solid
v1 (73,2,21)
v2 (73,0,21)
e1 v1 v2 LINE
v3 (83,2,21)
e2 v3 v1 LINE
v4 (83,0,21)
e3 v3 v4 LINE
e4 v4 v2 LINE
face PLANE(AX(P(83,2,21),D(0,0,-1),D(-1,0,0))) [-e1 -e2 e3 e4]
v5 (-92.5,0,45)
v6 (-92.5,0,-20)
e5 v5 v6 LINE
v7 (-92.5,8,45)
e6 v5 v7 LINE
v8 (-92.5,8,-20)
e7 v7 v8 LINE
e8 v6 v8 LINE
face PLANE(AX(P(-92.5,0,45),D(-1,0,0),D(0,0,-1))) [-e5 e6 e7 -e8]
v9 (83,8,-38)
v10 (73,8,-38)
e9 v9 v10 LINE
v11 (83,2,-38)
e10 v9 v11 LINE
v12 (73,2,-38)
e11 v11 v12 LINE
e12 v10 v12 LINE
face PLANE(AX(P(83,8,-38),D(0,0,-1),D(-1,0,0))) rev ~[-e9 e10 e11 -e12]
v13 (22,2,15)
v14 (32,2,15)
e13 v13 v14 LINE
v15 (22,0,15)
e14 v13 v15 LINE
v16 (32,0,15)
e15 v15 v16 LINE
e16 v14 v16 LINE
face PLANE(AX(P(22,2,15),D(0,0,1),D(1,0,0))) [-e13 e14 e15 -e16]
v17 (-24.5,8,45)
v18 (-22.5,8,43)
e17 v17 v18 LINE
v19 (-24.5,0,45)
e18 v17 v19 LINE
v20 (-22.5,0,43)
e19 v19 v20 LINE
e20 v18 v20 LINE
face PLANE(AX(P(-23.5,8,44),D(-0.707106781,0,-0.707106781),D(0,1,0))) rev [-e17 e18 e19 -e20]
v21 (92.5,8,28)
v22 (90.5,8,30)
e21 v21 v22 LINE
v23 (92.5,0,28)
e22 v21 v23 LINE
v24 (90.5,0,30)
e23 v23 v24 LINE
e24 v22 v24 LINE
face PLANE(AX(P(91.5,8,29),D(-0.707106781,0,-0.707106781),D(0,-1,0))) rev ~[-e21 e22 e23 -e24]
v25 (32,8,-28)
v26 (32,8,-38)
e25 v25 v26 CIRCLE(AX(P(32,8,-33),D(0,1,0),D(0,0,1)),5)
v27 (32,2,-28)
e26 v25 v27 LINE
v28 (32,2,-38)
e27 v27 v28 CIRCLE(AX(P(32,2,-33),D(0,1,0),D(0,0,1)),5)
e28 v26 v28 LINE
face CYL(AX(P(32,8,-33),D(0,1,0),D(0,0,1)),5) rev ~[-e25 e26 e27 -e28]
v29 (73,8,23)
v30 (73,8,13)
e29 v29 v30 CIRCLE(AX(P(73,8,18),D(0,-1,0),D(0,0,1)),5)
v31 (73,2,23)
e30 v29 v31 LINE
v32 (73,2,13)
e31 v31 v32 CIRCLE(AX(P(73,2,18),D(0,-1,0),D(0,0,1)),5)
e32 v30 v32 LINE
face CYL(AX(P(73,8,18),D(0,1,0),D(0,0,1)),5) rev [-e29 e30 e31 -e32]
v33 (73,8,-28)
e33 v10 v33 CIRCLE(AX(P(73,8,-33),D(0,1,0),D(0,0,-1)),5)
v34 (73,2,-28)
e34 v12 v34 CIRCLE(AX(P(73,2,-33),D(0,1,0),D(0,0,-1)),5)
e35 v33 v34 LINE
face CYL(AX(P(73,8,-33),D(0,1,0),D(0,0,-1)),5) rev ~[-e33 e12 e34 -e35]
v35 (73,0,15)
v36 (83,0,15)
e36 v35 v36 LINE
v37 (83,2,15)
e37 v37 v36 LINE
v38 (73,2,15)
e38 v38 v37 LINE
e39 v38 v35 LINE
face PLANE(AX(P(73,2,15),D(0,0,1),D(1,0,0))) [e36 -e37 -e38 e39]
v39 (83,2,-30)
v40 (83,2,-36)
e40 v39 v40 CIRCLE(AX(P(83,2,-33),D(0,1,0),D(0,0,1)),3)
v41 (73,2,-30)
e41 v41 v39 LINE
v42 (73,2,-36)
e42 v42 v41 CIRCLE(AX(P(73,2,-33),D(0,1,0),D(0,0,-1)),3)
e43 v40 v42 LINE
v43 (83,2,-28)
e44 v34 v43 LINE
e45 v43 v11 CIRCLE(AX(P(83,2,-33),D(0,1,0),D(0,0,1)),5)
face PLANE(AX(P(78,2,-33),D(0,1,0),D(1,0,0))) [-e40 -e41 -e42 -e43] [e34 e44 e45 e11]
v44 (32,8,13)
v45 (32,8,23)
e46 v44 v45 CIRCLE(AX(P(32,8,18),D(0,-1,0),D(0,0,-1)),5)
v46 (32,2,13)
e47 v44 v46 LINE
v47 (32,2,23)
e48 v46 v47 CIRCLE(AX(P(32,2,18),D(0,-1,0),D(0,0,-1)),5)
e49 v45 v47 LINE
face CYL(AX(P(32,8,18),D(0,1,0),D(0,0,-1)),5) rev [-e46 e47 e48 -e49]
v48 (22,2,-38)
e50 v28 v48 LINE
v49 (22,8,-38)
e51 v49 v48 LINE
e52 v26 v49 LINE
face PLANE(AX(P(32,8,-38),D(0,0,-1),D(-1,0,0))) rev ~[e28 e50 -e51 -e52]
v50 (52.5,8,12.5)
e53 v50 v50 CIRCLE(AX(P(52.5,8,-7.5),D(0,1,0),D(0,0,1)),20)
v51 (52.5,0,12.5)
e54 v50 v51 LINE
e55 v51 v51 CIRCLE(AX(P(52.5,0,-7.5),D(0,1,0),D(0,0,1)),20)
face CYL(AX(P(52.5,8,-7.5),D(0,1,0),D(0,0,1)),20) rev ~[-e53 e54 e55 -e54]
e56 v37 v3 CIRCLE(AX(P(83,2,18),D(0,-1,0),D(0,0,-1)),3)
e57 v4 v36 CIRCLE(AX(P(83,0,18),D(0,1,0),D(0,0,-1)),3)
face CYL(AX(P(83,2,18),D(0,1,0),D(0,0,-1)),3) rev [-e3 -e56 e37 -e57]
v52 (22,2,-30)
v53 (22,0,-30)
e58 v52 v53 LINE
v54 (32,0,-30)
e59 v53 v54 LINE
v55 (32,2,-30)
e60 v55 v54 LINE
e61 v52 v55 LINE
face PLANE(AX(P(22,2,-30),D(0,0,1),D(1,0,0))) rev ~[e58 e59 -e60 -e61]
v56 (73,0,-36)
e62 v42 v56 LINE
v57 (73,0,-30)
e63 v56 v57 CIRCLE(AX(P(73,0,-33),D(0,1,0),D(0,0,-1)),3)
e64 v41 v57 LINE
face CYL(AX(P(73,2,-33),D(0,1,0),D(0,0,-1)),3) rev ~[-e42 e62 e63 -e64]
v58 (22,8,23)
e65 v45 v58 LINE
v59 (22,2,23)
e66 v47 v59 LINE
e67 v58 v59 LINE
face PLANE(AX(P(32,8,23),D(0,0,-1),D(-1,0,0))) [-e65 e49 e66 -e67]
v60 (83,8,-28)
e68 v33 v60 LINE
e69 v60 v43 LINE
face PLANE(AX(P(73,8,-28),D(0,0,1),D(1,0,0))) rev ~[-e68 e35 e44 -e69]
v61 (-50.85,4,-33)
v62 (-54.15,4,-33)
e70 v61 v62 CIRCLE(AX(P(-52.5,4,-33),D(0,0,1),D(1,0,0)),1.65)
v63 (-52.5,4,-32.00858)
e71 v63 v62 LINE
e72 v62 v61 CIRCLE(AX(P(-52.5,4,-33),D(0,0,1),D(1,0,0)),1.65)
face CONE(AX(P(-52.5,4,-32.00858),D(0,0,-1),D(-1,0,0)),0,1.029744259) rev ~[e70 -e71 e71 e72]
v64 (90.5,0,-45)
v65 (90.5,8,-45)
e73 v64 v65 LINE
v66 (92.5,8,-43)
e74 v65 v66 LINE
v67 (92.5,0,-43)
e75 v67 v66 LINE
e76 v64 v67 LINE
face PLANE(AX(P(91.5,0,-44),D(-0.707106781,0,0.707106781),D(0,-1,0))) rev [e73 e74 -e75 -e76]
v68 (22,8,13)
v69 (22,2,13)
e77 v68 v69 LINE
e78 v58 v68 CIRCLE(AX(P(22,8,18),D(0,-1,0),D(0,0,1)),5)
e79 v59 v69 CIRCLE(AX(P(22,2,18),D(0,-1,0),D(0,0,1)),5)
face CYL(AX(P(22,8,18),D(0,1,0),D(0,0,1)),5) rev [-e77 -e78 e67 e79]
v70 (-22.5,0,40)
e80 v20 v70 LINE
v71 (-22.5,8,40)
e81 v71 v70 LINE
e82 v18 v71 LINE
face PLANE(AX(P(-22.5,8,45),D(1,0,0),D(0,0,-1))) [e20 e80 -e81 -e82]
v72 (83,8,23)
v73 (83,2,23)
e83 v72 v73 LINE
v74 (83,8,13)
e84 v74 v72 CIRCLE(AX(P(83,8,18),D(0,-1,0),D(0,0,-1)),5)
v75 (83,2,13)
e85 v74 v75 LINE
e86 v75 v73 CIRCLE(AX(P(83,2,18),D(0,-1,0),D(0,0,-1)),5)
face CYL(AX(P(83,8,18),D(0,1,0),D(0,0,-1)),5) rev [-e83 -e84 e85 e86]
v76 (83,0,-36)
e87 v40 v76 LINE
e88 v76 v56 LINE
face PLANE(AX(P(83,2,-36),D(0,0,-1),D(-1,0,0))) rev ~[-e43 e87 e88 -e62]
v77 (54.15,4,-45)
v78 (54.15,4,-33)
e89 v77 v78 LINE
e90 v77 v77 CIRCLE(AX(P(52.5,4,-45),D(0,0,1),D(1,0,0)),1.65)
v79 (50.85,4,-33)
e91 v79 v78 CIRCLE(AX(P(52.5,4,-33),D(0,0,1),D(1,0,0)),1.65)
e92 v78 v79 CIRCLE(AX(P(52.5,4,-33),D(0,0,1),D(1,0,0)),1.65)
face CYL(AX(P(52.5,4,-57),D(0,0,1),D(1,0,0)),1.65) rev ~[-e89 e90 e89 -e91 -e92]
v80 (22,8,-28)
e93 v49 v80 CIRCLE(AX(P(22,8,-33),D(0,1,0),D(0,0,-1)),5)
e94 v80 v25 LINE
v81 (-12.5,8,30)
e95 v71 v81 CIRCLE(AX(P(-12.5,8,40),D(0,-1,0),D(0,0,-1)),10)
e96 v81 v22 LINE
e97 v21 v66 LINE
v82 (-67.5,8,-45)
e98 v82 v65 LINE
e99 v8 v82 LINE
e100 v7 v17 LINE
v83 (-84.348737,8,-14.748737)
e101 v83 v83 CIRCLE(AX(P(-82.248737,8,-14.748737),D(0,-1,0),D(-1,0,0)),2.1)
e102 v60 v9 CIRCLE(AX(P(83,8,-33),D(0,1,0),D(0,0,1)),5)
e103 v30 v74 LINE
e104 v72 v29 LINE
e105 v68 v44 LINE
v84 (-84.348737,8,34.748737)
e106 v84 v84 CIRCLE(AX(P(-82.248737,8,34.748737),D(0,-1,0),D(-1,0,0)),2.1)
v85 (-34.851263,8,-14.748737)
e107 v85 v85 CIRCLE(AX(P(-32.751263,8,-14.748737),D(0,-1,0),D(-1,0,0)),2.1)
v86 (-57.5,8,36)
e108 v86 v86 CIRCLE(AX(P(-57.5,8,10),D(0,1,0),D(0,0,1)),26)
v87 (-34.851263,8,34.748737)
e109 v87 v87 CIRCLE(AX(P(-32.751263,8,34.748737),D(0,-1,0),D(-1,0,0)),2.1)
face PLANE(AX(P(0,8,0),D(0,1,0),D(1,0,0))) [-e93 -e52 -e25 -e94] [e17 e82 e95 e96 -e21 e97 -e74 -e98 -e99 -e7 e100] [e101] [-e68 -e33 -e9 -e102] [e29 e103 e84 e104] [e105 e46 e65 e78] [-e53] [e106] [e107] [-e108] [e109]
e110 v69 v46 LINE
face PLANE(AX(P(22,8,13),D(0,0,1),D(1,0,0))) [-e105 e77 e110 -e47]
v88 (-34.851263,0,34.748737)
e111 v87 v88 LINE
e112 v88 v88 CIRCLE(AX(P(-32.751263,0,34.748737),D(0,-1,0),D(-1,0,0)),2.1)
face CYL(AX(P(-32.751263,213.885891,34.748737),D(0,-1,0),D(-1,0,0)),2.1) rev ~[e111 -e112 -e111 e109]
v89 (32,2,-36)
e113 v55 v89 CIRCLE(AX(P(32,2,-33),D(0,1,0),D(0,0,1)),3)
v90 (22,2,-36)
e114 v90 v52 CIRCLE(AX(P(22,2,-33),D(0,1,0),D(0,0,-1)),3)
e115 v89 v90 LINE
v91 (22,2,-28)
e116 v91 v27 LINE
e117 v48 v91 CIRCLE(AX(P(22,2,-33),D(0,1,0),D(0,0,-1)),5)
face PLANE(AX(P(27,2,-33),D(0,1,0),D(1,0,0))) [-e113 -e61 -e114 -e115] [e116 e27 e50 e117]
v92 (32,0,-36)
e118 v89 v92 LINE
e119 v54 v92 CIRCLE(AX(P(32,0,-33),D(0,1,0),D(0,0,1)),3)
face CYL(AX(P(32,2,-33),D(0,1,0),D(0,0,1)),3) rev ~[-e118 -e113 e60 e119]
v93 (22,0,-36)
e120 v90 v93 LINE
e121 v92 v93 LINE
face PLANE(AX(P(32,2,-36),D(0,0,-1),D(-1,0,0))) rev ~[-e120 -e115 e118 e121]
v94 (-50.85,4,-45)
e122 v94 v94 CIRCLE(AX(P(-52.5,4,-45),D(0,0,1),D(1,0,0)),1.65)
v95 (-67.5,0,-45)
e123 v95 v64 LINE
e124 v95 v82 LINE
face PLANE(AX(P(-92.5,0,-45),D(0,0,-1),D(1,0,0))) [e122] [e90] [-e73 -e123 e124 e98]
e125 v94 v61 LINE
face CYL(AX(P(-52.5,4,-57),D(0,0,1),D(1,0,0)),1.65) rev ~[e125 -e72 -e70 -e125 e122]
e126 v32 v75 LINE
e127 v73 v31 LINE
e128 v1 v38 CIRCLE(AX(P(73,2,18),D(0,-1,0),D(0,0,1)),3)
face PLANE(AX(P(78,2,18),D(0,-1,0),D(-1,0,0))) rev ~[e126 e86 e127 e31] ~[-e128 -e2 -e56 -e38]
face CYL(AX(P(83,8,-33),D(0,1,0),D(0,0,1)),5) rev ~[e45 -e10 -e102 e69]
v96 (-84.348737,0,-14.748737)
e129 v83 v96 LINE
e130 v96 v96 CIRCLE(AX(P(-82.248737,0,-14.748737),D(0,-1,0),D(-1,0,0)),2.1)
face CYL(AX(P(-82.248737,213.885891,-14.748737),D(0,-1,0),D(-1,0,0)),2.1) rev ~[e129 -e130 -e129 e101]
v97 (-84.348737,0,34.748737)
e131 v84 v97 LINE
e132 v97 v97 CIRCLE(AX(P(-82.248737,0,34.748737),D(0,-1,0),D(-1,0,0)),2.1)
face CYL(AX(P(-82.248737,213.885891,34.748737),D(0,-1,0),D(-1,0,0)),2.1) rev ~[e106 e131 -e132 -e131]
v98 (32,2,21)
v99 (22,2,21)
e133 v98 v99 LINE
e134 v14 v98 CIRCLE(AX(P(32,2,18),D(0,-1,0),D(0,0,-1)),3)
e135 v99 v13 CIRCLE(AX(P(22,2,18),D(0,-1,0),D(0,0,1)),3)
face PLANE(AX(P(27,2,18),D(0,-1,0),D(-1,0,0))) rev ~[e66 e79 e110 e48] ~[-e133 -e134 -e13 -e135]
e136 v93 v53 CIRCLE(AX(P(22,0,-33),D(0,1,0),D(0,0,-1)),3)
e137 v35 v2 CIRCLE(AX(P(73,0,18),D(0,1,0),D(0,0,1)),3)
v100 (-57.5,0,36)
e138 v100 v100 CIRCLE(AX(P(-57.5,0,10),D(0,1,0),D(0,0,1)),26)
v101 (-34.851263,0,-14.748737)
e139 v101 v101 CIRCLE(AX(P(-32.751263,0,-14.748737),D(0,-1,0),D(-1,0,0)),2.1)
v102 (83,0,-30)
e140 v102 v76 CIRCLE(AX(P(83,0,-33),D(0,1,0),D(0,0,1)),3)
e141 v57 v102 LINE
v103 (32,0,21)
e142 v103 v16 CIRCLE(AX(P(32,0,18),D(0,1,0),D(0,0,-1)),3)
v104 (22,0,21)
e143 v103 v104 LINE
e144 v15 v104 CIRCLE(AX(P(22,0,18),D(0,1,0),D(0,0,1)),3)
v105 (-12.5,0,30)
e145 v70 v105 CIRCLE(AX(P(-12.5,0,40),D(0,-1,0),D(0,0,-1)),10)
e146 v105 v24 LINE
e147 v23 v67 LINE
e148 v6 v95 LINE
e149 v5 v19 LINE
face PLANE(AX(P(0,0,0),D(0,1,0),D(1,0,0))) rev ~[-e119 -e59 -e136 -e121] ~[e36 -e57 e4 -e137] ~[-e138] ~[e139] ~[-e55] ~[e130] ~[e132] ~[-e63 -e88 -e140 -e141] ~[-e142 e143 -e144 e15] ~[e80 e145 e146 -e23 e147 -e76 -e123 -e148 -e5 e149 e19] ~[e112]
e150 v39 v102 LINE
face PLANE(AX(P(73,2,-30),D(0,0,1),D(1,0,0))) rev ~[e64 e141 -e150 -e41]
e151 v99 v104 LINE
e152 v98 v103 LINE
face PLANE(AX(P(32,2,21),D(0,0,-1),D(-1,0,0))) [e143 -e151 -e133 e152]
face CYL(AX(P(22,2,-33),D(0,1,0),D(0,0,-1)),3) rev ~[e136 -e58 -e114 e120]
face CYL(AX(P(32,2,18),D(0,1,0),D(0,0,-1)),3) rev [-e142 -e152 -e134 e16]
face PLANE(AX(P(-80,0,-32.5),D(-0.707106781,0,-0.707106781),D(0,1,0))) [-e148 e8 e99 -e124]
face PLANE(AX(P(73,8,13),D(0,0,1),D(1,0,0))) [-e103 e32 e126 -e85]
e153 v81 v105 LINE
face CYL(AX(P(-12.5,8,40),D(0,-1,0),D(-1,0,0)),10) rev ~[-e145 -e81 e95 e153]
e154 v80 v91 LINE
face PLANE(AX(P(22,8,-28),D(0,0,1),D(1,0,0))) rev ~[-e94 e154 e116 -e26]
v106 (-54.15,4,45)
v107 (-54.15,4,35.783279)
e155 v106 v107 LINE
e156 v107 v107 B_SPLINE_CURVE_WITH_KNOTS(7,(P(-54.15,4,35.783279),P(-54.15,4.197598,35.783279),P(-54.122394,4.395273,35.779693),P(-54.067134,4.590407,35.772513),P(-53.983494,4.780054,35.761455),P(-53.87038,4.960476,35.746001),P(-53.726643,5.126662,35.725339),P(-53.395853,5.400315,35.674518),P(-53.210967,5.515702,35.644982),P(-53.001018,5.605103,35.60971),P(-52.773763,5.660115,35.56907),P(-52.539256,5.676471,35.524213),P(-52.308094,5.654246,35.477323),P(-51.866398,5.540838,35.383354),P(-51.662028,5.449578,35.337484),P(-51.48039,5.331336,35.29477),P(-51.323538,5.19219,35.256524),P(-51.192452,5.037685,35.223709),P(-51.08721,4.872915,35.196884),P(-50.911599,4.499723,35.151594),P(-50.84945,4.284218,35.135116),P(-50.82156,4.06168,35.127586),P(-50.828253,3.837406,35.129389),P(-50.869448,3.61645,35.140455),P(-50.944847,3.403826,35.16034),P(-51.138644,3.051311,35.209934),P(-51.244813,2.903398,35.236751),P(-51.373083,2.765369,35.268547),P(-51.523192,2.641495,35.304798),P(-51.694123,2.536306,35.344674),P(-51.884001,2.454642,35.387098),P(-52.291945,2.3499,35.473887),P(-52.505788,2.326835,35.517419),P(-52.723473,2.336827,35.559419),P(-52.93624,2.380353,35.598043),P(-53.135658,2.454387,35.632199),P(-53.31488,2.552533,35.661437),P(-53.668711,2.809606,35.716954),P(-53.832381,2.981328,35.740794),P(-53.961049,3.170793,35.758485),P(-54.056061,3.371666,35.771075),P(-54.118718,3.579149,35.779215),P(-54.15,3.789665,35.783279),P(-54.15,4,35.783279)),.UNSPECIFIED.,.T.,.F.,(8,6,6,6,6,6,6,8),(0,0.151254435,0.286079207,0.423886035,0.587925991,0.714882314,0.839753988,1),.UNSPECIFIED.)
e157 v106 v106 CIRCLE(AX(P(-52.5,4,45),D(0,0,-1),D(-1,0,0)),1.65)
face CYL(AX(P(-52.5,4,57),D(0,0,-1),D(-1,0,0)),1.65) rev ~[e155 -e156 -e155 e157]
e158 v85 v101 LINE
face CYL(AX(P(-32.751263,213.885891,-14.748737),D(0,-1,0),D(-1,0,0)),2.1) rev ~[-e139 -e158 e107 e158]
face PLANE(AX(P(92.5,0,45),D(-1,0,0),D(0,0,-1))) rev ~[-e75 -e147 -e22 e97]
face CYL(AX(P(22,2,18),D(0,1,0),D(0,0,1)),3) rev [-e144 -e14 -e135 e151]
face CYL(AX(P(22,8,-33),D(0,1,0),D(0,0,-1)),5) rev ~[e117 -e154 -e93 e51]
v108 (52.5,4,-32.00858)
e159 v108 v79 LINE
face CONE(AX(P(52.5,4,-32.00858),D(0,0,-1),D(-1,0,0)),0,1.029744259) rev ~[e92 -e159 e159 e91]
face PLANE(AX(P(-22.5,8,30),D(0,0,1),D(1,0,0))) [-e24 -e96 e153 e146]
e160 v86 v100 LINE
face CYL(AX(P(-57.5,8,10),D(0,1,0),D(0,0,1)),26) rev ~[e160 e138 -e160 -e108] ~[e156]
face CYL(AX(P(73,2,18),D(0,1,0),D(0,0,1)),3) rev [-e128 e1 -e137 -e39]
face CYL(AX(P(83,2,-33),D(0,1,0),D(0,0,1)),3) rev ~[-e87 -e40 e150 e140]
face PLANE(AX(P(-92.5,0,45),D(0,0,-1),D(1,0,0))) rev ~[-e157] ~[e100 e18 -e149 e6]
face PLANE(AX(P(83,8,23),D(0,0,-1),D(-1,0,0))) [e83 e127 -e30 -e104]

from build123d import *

# Parameters (mm, degrees)
SKETCH_2_W             = 185
SKETCH_2_H             = 90
EXTRUDE_1_DEPTH        = 8
SKETCH_4_W             = 115
SKETCH_4_H             = 15
CUT_EXTRUDE_7_DEPTH    = 104.175820811
SKETCH_5_R             = 26
CUT_EXTRUDE_8_DEPTH    = 104.175820811
HOLE_WIZARD_M5_1_D     = 4.2
SKETCH_10_R            = 20
CUT_EXTRUDE_9_DEPTH    = 104.175820811
CUT_EXTRUDE_15_DEPTH   = 6
CUT_EXTRUDE_16_DEPTH   = 104.040040761
HOLE_WIZARD_M4_1_D     = 3.3
HOLE_WIZARD_M4_1_DEPTH = 12
HOLE_WIZARD_M4_1_TIP   = 0.991420021
HOLE_WIZARD_M4_2_D     = 3.3
HOLE_WIZARD_M4_2_DEPTH = 12
HOLE_WIZARD_M4_2_TIP   = 0.991420021
CHAMFER_1_SIZE         = 25
CHAMFER_2_SIZE         = 2
FILLET_1_R             = 10


with BuildPart() as part:
    # 草图2 → 凸台-拉伸1 (new body)
    with BuildSketch(Plane(origin=(0, 0, 0), x_dir=(1, 0, 0), z_dir=(0, 1, 0))):
        Rectangle(SKETCH_2_W, SKETCH_2_H)
    extrude(amount=EXTRUDE_1_DEPTH)

    # 草图4 → 切除-拉伸7 (cut, through all)
    with BuildSketch(Plane(origin=(0, 8, 0), x_dir=(1, 0, 0), z_dir=(0, 1, 0))):
        with Locations((35, -37.5)):
            Rectangle(SKETCH_4_W, SKETCH_4_H)
    extrude(amount=-CUT_EXTRUDE_7_DEPTH, mode=Mode.SUBTRACT)

    # 草图5 → 切除-拉伸8 (cut, through all)
    with BuildSketch(Plane(origin=(0, 8, 0), x_dir=(1, 0, 0), z_dir=(0, 1, 0))):
        with Locations(Location((-57.5, -10, 0), (0, 0, 270))):
            Circle(SKETCH_5_R)
    extrude(amount=-CUT_EXTRUDE_8_DEPTH, mode=Mode.SUBTRACT)

    # M5 螺纹孔1 (through all)
    with Locations(Plane(origin=(0, 8, 0), x_dir=(1, 0, 0), z_dir=(0, 1, 0))):
        with Locations((-82.248737342, 14.748737342), (-32.751262658, 14.748737342), (-32.751262658, -34.748737342), (-82.248737342, -34.748737342), (-57.5, -10)):
            Hole(HOLE_WIZARD_M5_1_D / 2)

    # 草图10 → 切除-拉伸9 (cut, through all)
    with BuildSketch(Plane(origin=(0, 8, 0), x_dir=(1, 0, 0), z_dir=(0, 1, 0))):
        with Locations(Location((52.5, 7.5, 0), (0, 0, 270))):
            Circle(SKETCH_10_R)
    extrude(amount=-CUT_EXTRUDE_9_DEPTH, mode=Mode.SUBTRACT)

    # 草图15 → 切除-拉伸15 (cut)
    with BuildSketch(Plane(origin=(0, 8, 0), x_dir=(1, 0, 0), z_dir=(0, 1, 0))):
        with BuildLine():
            Line((73, -13), (83, -13))
            ThreePointArc((83, -13), (88, -18), (83, -23))
            Line((83, -23), (73, -23))
            ThreePointArc((73, -23), (68, -18), (73, -13))
        make_face()
        with BuildLine():
            Line((73, 28), (83, 28))
            ThreePointArc((83, 28), (88, 33), (83, 38))
            Line((83, 38), (73, 38))
            ThreePointArc((73, 38), (68, 33), (73, 28))
        make_face()
        with BuildLine():
            Line((22, -13), (32, -13))
            ThreePointArc((32, -13), (37, -18), (32, -23))
            Line((32, -23), (22, -23))
            ThreePointArc((22, -23), (17, -18), (22, -13))
        make_face()
        with BuildLine():
            Line((22, 28), (32, 28))
            ThreePointArc((32, 28), (37, 33), (32, 38))
            Line((32, 38), (22, 38))
            ThreePointArc((22, 38), (17, 33), (22, 28))
        make_face()
    extrude(amount=-CUT_EXTRUDE_15_DEPTH, mode=Mode.SUBTRACT)

    # 草图16 → 切除-拉伸16 (cut, through all)
    with BuildSketch(Plane(origin=(0, 2, 0), x_dir=(1, 0, 0), z_dir=(0, 1, 0))):
        with BuildLine():
            Line((73, -15), (83, -15))
            ThreePointArc((83, -15), (86, -18), (83, -21))
            Line((83, -21), (73, -21))
            ThreePointArc((73, -21), (70, -18), (73, -15))
        make_face()
        with BuildLine():
            Line((73, 30), (83, 30))
            ThreePointArc((83, 30), (86, 33), (83, 36))
            Line((83, 36), (73, 36))
            ThreePointArc((73, 36), (70, 33), (73, 30))
        make_face()
        with BuildLine():
            Line((22, -15), (32, -15))
            ThreePointArc((32, -15), (35, -18), (32, -21))
            Line((32, -21), (22, -21))
            ThreePointArc((22, -21), (19, -18), (22, -15))
        make_face()
        with BuildLine():
            Line((22, 30), (32, 30))
            ThreePointArc((32, 30), (35, 33), (32, 36))
            Line((32, 36), (22, 36))
            ThreePointArc((22, 36), (19, 33), (22, 30))
        make_face()
    extrude(amount=-CUT_EXTRUDE_16_DEPTH, mode=Mode.SUBTRACT)

    # M4 螺纹孔1
    with Locations(Plane(origin=(0, 0, -45), x_dir=(-1, 0, 0), z_dir=(0, 0, -1))):
        with Locations((-52.5, 4), (52.5, 4)):
            Hole(HOLE_WIZARD_M4_1_D / 2, depth=HOLE_WIZARD_M4_1_DEPTH)
            with Locations((0, 0, -(HOLE_WIZARD_M4_1_DEPTH + HOLE_WIZARD_M4_1_TIP / 2))):  # 118° drill point
                Cone(0, HOLE_WIZARD_M4_1_D / 2, HOLE_WIZARD_M4_1_TIP, mode=Mode.SUBTRACT)

    # M4 螺纹孔2
    with Locations(Plane.XY.offset(45)):
        with Locations((-52.5, 4)):
            Hole(HOLE_WIZARD_M4_2_D / 2, depth=HOLE_WIZARD_M4_2_DEPTH)
            with Locations((0, 0, -(HOLE_WIZARD_M4_2_DEPTH + HOLE_WIZARD_M4_2_TIP / 2))):  # 118° drill point
                Cone(0, HOLE_WIZARD_M4_2_D / 2, HOLE_WIZARD_M4_2_TIP, mode=Mode.SUBTRACT)

    # 倒角1
    chamfer_1_edges = [part.edges().sort_by_distance(p)[0] for p in [
        (-92.5, 4, -45),
    ]]
    chamfer(chamfer_1_edges, length=CHAMFER_1_SIZE)

    # 倒角2
    chamfer_2_edges = [part.edges().sort_by_distance(p)[0] for p in [
        (92.5, 4, 30),
        (-22.5, 4, 45),
        (92.5, 4, -45),
    ]]
    chamfer(chamfer_2_edges, length=CHAMFER_2_SIZE)

    # 圆角1
    fillet_1_edges = [part.edges().sort_by_distance(p)[0] for p in [
        (-22.5, 4, 30),
    ]]
    fillet(fillet_1_edges, radius=FILLET_1_R)


solid = part.part
